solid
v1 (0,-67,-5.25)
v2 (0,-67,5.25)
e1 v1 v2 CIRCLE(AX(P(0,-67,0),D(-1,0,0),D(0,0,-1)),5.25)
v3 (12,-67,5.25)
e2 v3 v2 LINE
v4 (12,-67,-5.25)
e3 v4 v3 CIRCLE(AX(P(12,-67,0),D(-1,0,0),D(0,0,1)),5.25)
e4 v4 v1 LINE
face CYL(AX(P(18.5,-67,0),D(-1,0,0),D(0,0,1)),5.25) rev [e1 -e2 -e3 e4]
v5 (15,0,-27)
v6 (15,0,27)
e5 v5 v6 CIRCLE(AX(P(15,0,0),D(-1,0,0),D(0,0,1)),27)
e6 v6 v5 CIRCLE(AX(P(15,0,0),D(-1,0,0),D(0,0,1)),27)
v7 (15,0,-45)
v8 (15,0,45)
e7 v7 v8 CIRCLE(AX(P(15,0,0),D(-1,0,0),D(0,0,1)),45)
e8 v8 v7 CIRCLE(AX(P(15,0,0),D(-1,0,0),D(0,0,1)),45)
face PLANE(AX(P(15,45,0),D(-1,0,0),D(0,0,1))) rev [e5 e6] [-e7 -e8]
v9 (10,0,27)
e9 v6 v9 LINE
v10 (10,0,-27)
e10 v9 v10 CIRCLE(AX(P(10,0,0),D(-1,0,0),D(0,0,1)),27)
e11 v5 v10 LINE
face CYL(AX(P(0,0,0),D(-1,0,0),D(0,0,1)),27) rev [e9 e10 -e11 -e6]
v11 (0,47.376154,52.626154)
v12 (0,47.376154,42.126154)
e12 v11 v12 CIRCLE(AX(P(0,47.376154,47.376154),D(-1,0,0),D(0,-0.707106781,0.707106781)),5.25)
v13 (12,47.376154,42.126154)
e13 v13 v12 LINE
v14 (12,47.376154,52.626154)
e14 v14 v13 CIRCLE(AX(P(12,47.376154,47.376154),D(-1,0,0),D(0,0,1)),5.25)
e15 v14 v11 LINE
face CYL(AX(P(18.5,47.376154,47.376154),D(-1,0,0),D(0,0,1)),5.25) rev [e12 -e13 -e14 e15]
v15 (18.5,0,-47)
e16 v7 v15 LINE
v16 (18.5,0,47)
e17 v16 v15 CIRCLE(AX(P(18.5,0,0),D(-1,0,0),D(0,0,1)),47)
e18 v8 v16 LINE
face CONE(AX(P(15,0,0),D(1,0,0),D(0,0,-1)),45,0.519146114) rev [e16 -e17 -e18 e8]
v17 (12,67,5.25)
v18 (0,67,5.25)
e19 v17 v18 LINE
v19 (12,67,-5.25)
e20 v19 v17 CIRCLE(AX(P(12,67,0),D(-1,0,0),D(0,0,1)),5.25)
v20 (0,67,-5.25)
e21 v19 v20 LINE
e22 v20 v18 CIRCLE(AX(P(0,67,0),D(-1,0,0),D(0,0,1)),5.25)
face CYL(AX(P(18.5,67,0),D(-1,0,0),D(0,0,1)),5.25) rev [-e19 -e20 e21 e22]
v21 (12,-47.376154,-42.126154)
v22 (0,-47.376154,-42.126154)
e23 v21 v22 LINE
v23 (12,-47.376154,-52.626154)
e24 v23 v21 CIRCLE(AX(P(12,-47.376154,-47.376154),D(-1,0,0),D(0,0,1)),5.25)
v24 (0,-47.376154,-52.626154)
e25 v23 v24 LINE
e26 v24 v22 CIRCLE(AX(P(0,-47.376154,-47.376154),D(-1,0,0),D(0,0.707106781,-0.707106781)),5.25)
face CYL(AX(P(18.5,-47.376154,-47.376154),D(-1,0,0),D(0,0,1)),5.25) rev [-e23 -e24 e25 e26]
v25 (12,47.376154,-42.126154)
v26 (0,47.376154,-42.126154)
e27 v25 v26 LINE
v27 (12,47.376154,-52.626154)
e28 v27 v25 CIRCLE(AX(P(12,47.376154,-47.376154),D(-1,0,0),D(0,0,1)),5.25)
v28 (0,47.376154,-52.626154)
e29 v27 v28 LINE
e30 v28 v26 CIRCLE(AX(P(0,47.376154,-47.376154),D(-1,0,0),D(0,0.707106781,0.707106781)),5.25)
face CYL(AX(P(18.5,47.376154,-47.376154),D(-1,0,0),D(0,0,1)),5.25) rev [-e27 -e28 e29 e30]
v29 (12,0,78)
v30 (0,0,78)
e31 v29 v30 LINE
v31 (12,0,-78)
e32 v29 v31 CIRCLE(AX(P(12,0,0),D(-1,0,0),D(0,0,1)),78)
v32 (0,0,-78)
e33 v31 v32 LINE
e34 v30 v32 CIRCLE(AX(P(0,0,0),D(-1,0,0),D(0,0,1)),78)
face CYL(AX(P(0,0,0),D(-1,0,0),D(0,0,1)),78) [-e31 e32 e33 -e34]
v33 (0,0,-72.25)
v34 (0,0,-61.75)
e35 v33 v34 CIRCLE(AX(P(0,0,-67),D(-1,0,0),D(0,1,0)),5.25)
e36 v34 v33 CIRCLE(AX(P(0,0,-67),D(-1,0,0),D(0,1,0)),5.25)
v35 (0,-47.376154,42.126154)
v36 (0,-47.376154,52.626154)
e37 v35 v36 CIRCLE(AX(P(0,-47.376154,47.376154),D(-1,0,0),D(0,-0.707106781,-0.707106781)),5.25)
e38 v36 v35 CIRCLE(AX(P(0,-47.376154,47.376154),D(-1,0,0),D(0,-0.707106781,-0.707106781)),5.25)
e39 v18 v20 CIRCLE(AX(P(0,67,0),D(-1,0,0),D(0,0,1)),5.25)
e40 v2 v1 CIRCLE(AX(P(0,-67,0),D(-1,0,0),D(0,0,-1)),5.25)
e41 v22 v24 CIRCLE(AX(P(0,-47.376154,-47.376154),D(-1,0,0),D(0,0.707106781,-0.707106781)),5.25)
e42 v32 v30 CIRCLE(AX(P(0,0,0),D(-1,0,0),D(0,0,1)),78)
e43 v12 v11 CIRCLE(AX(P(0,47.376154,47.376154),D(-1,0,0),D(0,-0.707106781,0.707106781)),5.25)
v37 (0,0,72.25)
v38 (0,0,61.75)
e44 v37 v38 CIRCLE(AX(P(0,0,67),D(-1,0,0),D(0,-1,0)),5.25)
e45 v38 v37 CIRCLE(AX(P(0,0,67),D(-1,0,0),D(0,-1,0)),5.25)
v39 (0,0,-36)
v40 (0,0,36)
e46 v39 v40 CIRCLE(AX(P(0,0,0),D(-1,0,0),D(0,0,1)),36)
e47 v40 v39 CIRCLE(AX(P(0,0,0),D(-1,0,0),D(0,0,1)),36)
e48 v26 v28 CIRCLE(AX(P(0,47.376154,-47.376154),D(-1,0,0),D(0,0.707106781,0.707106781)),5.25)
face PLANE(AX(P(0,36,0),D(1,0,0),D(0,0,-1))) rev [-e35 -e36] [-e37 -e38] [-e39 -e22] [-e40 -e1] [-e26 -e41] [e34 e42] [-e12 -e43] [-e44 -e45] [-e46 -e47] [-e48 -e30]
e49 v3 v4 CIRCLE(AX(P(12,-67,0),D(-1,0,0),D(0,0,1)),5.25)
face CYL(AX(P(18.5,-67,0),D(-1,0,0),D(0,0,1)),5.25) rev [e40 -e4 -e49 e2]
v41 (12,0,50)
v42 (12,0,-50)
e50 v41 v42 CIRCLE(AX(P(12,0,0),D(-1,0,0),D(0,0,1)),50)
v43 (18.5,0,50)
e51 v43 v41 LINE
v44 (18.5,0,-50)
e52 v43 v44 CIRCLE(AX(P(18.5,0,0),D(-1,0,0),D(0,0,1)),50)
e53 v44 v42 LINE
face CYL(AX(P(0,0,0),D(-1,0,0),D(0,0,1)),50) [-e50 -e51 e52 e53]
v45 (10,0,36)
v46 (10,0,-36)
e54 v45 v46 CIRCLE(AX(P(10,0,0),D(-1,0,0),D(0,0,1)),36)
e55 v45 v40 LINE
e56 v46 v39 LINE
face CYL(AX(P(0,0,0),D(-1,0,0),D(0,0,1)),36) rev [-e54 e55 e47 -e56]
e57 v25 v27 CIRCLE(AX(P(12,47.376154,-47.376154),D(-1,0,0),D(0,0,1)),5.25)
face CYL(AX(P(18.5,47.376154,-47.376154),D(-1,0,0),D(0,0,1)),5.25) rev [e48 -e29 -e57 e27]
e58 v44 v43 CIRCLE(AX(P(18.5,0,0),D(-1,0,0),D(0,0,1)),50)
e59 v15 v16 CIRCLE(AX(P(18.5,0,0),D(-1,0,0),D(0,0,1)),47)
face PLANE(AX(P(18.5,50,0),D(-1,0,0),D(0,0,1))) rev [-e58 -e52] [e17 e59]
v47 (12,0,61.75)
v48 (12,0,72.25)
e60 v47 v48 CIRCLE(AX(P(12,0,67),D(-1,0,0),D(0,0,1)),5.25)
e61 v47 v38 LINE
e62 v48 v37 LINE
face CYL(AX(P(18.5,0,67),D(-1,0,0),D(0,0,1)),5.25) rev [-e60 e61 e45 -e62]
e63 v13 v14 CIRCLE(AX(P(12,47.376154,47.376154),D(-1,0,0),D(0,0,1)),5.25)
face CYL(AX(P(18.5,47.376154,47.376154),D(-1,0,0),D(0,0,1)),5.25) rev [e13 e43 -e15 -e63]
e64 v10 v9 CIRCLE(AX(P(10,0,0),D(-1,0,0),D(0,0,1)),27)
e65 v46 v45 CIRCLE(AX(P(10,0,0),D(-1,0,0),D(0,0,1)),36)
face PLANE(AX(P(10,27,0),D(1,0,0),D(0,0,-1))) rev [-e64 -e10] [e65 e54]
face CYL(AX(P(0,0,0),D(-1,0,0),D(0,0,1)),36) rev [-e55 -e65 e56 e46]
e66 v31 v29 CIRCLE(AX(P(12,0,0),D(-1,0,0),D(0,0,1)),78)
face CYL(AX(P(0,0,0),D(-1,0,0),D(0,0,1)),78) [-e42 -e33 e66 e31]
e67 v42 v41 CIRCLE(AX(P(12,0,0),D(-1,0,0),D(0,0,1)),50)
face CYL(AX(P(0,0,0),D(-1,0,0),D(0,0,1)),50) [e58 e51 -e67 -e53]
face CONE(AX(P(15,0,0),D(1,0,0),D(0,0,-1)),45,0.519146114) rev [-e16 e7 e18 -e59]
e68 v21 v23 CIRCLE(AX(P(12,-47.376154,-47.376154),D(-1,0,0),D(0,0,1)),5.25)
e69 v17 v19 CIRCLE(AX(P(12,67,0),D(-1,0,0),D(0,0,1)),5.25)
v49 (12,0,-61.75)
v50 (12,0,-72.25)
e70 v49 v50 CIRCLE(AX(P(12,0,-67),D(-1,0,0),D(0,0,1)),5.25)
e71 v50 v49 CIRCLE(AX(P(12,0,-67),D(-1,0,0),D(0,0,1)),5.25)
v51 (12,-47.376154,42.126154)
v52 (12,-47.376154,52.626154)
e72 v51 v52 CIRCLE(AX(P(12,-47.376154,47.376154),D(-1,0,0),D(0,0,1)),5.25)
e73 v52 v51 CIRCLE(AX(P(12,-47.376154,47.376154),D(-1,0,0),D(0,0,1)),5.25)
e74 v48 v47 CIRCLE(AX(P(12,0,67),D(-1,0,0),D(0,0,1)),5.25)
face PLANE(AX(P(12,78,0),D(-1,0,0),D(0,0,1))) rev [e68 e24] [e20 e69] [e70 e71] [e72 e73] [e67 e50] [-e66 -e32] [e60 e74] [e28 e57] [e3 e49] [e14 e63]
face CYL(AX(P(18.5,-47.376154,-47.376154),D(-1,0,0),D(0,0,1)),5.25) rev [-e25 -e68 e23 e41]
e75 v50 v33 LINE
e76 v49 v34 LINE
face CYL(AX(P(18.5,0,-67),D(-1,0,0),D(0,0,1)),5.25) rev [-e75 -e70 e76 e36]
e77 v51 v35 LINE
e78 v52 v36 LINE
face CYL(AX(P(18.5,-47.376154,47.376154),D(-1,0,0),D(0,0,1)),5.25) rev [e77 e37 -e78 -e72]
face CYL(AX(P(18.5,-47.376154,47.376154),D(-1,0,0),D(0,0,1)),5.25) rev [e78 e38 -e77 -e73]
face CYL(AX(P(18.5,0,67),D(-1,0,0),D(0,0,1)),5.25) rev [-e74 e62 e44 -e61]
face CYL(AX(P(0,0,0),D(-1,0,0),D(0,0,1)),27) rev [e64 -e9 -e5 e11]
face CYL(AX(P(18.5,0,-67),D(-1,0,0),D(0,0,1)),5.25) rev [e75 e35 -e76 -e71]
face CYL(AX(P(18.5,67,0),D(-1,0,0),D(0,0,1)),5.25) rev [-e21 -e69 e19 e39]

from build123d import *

# Parameters (mm, degrees)
SKETCH2_R          = 5.25
CUT_EXTRUDE1_DEPTH = 112.849228875
CIRPATTERN1_COUNT  = 8


with BuildPart() as part:
    # Sketch1 → Revolve1 (revolve)
    with BuildSketch(Plane.XY, mode=Mode.PRIVATE) as revolve1_sk:
        Polygon((0, 36), (0, 78), (12, 78), (12, 50), (18.5, 50), (18.5, 47), (15, 45), (15, 27), (10, 27), (10, 36), align=None)
    revolve(revolve1_sk.sketch.rotate(Axis((0, 0, 0), (1, 0, 0)), 90), axis=Axis((0, 0, 0), (1, 0, 0)))

    # Sketch2 → Cut-Extrude1 (cut, through all)
    with BuildSketch(Plane.ZY):
        with Locations((0, 67)):
            Circle(SKETCH2_R)
    cut_extrude1 = extrude(amount=-CUT_EXTRUDE1_DEPTH, mode=Mode.SUBTRACT)

    # CirPattern1: Cut-Extrude1 ×8 about axis
    cirpattern1_axis = Axis((0, 0, 0), (1, 0, 0))
    for i in range(1, CIRPATTERN1_COUNT):
        add(cut_extrude1.rotate(cirpattern1_axis, i * 360 / CIRPATTERN1_COUNT), mode=Mode.SUBTRACT)


solid = part.part
